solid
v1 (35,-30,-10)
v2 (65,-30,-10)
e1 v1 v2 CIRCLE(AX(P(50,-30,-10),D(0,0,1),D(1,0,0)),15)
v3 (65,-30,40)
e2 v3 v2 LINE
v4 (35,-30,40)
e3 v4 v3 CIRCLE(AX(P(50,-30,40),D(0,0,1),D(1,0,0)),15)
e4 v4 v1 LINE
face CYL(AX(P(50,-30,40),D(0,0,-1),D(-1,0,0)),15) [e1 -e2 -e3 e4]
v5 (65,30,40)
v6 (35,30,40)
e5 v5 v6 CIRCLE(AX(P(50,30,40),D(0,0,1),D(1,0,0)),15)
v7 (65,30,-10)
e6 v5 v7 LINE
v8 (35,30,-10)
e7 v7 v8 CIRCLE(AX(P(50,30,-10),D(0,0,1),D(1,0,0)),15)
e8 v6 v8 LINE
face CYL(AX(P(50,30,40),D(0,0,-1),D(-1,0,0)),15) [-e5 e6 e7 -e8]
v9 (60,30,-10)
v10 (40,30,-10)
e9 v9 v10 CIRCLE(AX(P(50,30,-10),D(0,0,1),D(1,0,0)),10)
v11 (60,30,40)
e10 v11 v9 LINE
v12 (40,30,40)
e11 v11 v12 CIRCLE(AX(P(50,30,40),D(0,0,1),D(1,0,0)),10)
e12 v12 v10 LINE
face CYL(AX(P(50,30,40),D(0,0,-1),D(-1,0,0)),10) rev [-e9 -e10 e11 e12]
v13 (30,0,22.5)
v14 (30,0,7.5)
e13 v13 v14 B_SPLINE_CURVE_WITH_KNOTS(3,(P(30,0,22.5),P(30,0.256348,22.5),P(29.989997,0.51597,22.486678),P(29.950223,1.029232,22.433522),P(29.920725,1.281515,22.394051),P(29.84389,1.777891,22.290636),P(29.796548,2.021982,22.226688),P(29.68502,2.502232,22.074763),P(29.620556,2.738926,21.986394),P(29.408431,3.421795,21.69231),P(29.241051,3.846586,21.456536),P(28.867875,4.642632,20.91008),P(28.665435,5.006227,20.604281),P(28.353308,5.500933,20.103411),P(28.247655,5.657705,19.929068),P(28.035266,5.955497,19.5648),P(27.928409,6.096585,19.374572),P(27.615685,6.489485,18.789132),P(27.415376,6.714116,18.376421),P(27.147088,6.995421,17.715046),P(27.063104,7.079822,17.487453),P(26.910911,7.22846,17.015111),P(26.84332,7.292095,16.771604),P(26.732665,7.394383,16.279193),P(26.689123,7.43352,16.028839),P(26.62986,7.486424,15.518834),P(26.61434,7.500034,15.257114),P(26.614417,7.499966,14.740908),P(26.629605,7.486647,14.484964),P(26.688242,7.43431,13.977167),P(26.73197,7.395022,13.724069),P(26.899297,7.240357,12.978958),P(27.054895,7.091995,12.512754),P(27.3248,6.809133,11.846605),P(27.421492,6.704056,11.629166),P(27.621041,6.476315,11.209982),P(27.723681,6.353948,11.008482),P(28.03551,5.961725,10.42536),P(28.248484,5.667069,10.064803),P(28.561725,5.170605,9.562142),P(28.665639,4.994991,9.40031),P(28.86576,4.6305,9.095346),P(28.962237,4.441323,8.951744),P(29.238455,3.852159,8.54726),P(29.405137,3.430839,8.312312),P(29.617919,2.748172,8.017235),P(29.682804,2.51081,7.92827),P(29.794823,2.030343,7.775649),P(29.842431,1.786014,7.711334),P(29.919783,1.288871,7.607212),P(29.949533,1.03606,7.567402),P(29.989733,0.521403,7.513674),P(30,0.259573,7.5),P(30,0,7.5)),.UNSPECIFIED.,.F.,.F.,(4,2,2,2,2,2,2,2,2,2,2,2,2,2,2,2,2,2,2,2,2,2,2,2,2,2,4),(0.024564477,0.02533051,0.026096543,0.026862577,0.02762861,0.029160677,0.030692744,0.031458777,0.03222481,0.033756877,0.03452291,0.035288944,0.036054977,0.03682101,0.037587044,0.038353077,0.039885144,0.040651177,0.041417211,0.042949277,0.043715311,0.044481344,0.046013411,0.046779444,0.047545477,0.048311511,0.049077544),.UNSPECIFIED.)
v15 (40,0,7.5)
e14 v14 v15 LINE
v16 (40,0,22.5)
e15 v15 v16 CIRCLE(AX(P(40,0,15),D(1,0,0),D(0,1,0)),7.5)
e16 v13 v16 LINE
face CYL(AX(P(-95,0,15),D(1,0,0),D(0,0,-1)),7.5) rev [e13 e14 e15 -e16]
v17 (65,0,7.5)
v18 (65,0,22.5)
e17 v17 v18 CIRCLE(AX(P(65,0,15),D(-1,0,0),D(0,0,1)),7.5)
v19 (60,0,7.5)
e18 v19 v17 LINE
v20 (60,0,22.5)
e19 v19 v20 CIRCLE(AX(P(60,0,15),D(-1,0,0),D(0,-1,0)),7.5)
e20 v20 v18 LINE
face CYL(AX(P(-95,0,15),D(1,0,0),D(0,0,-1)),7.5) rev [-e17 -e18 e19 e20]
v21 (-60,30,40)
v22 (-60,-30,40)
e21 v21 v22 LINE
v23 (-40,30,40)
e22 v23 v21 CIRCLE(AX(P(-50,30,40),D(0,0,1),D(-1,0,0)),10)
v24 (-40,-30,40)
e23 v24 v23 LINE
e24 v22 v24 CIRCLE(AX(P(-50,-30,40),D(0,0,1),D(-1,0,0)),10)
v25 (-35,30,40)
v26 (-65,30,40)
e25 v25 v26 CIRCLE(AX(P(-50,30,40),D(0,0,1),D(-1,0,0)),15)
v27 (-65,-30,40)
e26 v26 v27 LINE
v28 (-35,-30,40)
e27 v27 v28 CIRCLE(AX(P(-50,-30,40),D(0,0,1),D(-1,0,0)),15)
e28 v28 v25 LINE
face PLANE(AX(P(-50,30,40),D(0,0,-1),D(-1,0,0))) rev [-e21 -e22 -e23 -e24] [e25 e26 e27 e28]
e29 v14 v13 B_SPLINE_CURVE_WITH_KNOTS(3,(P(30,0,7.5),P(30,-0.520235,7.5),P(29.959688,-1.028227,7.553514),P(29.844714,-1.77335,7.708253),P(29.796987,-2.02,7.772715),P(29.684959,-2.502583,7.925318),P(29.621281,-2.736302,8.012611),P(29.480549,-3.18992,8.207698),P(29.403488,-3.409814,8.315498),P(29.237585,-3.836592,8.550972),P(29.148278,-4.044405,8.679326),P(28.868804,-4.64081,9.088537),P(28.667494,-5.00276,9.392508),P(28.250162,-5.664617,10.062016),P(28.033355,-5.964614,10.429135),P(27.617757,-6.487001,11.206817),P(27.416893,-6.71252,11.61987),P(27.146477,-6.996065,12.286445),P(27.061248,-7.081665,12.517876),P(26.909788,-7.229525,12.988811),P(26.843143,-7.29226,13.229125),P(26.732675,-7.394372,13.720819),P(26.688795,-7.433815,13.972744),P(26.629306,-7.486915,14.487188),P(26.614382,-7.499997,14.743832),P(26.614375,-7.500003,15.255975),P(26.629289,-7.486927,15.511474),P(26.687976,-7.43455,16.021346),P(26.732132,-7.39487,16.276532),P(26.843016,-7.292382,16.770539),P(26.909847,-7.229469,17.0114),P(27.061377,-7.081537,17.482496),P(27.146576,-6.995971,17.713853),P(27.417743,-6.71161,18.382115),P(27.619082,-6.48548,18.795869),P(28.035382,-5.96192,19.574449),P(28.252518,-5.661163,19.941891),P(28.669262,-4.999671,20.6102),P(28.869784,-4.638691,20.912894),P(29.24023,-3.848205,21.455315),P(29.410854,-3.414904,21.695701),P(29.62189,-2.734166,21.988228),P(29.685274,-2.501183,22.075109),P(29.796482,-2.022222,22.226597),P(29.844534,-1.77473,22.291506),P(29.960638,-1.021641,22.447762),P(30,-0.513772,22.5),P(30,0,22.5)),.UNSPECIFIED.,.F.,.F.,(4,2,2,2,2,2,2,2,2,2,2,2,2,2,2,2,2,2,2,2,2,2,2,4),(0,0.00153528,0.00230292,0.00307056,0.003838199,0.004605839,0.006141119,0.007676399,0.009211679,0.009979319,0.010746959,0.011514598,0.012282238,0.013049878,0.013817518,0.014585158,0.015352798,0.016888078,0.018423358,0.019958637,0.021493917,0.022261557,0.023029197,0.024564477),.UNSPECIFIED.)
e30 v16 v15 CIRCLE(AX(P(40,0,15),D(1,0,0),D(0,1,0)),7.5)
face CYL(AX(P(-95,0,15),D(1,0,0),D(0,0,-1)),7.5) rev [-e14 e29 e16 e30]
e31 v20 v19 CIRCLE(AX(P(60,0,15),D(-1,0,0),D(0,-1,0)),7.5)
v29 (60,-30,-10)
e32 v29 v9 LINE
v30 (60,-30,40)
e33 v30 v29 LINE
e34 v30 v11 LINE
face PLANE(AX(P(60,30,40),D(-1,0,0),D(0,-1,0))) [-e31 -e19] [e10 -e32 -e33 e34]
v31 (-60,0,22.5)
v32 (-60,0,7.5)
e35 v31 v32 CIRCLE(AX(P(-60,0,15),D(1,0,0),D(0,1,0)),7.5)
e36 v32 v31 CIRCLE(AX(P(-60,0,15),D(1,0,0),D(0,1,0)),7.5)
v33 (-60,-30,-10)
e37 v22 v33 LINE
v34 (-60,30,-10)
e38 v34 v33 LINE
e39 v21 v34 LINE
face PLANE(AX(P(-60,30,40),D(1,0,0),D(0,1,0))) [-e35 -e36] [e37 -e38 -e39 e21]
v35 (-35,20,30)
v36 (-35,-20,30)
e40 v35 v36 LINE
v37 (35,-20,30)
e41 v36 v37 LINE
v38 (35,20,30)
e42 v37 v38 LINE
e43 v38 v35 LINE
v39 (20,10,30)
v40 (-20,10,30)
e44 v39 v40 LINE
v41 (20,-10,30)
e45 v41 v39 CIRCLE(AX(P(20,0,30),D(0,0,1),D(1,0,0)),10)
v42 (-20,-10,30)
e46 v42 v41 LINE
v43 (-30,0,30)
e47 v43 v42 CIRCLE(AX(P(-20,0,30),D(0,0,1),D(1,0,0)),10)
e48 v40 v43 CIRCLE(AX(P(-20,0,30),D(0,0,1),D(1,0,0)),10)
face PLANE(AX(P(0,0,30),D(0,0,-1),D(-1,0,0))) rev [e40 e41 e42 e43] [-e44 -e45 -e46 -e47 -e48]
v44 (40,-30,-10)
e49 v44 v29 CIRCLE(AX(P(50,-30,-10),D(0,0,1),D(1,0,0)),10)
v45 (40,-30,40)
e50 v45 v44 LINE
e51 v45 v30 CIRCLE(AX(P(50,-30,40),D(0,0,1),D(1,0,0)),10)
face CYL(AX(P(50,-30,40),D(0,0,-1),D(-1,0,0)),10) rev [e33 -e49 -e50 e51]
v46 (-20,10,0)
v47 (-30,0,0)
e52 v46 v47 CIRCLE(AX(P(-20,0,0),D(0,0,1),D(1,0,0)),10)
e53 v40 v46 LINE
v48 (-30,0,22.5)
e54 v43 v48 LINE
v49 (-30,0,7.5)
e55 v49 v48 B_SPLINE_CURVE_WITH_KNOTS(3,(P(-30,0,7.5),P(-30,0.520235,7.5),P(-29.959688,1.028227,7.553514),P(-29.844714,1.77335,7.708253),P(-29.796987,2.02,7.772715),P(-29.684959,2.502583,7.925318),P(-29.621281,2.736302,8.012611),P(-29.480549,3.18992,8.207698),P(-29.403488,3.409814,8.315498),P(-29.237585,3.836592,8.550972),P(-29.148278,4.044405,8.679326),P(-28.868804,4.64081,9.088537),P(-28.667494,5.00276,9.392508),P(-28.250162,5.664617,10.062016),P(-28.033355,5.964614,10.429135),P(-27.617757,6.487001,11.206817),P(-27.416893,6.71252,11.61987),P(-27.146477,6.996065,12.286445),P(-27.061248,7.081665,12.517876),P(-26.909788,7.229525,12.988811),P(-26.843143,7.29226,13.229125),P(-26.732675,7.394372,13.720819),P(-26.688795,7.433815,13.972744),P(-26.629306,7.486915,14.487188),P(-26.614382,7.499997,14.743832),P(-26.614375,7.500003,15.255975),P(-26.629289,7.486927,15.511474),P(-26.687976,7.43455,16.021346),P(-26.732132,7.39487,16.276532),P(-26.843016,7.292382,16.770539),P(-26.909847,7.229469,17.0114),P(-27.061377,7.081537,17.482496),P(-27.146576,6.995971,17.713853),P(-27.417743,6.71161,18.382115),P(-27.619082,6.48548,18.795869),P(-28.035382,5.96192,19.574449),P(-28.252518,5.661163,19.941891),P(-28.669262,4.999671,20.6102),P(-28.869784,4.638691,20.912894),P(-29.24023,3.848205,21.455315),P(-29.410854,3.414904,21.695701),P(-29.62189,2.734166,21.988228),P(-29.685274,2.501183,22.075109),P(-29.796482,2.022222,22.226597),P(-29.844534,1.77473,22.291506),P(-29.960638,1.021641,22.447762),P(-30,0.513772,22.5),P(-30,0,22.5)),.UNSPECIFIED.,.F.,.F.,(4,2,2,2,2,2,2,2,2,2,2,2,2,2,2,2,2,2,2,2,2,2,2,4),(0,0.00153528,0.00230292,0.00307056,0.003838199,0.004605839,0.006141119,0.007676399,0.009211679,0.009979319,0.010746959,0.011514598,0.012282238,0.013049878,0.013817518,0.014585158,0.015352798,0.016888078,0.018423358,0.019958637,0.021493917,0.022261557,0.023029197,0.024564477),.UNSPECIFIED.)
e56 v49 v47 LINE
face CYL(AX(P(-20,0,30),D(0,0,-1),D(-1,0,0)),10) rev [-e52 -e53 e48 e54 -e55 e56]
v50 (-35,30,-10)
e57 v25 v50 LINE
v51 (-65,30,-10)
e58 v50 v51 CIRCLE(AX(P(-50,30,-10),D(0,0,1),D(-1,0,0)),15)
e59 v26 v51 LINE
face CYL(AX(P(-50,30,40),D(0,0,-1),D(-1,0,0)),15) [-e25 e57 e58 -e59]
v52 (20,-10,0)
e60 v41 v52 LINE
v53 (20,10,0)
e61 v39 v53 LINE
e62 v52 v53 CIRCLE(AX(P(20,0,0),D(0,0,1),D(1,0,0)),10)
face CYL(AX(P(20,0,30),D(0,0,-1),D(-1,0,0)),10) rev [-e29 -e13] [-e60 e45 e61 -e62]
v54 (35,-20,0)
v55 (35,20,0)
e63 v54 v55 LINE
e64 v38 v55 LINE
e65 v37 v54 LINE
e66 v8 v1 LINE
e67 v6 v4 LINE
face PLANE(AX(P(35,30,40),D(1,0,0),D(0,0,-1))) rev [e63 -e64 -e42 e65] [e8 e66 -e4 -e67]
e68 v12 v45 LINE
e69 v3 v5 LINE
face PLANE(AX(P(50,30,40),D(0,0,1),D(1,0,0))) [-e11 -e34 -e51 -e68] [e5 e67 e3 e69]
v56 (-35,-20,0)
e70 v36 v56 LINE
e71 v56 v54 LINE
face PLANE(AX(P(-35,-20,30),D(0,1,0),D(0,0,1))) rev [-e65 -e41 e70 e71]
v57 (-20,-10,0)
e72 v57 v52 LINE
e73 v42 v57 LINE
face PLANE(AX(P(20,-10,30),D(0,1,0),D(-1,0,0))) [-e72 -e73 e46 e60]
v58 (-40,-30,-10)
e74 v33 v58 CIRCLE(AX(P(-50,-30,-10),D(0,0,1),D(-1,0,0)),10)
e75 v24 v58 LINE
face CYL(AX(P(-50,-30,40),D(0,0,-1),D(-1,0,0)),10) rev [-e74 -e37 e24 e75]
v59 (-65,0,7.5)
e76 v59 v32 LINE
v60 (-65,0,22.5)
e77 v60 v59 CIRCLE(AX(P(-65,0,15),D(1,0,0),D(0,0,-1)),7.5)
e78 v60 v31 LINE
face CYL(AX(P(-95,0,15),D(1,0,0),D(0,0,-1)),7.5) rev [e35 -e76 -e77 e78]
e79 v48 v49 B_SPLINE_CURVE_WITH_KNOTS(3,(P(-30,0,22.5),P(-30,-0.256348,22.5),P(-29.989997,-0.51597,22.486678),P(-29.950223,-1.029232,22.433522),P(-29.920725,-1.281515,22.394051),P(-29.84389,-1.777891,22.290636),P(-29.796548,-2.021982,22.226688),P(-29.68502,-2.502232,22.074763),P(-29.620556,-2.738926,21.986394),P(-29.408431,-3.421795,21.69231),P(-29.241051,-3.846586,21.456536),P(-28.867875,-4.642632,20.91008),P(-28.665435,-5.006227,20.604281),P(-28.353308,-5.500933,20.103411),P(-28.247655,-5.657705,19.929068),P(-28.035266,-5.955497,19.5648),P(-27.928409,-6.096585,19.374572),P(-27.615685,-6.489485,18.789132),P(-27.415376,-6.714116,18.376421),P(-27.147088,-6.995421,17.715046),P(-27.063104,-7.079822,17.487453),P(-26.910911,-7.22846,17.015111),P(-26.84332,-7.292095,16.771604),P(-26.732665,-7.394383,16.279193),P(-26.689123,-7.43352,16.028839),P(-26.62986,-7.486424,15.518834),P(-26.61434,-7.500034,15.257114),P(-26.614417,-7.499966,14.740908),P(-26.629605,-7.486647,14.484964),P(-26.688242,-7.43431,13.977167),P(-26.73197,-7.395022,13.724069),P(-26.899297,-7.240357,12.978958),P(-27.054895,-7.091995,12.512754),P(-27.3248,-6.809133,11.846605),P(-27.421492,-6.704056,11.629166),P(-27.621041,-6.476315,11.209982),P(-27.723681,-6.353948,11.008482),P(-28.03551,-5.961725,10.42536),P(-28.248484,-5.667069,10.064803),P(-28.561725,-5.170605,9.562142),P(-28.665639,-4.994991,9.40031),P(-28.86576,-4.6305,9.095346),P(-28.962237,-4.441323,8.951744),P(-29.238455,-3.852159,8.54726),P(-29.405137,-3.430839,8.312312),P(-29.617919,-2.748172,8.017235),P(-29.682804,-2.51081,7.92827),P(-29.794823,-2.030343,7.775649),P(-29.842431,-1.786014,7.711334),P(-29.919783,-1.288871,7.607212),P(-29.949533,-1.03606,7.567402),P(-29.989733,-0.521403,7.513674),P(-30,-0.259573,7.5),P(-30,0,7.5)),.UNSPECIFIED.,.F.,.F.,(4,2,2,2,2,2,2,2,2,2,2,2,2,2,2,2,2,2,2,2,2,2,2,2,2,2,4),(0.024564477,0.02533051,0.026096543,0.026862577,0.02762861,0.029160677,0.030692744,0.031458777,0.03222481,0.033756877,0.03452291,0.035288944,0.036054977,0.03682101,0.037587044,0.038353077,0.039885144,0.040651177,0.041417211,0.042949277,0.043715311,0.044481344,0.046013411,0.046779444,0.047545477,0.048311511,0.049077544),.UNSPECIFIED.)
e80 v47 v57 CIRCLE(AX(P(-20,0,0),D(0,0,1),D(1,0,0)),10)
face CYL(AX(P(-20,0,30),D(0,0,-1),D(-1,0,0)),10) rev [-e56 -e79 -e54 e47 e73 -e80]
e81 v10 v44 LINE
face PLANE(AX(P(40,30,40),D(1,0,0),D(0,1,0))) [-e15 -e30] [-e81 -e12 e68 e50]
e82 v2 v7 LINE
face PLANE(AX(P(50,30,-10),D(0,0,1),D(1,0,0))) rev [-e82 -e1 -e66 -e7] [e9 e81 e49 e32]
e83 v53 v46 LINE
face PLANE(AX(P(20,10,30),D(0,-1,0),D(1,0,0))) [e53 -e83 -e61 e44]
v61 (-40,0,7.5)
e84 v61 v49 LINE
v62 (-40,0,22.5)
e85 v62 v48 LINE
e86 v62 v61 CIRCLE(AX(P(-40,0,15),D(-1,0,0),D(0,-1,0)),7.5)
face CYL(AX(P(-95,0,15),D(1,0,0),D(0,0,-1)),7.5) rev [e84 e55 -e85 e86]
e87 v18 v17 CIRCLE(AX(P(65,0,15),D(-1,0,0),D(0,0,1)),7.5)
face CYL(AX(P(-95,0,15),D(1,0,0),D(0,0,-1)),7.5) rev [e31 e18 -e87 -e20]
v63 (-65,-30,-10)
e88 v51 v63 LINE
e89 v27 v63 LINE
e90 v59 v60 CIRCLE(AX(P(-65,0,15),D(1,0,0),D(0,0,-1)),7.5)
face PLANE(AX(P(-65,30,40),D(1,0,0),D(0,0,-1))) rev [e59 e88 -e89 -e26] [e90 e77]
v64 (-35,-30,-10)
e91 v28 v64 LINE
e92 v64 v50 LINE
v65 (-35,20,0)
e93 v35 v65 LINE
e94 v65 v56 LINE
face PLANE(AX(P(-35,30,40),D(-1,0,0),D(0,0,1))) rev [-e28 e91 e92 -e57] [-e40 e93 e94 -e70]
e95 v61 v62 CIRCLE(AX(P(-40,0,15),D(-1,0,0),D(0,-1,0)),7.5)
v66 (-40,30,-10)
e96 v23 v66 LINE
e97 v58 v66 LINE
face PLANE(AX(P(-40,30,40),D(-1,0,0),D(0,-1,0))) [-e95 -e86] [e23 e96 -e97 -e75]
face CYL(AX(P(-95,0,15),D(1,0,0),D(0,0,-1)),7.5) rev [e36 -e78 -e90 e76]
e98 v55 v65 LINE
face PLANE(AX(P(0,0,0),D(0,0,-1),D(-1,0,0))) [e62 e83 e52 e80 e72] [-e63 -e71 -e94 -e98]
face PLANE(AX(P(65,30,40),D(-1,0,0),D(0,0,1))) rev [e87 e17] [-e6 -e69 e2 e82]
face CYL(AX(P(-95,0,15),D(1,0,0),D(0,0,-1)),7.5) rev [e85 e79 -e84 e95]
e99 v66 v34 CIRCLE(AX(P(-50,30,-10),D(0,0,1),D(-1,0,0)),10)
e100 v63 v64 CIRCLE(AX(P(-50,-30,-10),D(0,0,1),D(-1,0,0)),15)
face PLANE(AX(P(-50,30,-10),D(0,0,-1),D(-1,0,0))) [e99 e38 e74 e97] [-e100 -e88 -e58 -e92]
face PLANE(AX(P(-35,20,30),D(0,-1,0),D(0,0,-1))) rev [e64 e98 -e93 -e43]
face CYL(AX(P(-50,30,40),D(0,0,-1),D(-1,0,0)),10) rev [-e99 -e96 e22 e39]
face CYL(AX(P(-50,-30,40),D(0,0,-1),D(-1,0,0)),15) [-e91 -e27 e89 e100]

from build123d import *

# Parameters (mm, degrees)
CENTRE_BLOCK_PROFILE_W = 70
CENTRE_BLOCK_PROFILE_H = 40
CENTRE_BLOCK_DEPTH     = 30
END_LOOPS_DEPTH        = 25
CROSS_HOLE_PROFILE_R   = 7.5
CROSS_HOLE_15_DEPTH    = 95


with BuildPart() as part:
    # Centre Block Profile → Centre Block (new body)
    with BuildSketch(Plane.XY):
        Rectangle(CENTRE_BLOCK_PROFILE_W, CENTRE_BLOCK_PROFILE_H)
        with BuildLine():
            Line((20, -10), (-20, -10))
            ThreePointArc((-20, -10), (-30, 0), (-20, 10))
            Line((-20, 10), (20, 10))
            ThreePointArc((20, 10), (30, 0), (20, -10))
        make_face(mode=Mode.SUBTRACT)
    extrude(amount=CENTRE_BLOCK_DEPTH)

    # End Loops Profile → End Loops (add, symmetric)
    # profile 1 of 2: a face of its own
    with BuildSketch(Plane.XY.offset(15)):
        with BuildLine():
            Line((65, 30), (65, -30))
            ThreePointArc((65, -30), (50, -45), (35, -30))
            Line((35, -30), (35, 30))
            ThreePointArc((35, 30), (50, 45), (65, 30))
        make_face()
        with BuildLine():
            Line((60, 30), (60, -30))
            ThreePointArc((60, -30), (50, -40), (40, -30))
            Line((40, -30), (40, 30))
            ThreePointArc((40, 30), (50, 40), (60, 30))
        make_face(mode=Mode.SUBTRACT)
    # profile 2 of 2: a face of its own
    with BuildSketch(Plane.XY.offset(15)):
        with BuildLine():
            Line((-65, 30), (-65, -30))
            ThreePointArc((-65, -30), (-50, -45), (-35, -30))
            Line((-35, -30), (-35, 30))
            ThreePointArc((-35, 30), (-50, 45), (-65, 30))
        make_face()
        with BuildLine():
            Line((-40, 30), (-40, -30))
            ThreePointArc((-40, -30), (-50, -40), (-60, -30))
            Line((-60, -30), (-60, 30))
            ThreePointArc((-60, 30), (-50, 40), (-40, 30))
        make_face(mode=Mode.SUBTRACT)
    extrude(amount=END_LOOPS_DEPTH, both=True)

    # Cross Hole Profile → Cross Hole Ø15 (cut, symmetric)
    with BuildSketch(Plane(origin=(0, 0, 0), x_dir=(0, 0, -1), z_dir=(1, 0, 0))):
        with Locations(Location((-15, 0, 0), (0, 0, 270))):
            Circle(CROSS_HOLE_PROFILE_R)
    extrude(amount=CROSS_HOLE_15_DEPTH, both=True, mode=Mode.SUBTRACT)


solid = part.part
